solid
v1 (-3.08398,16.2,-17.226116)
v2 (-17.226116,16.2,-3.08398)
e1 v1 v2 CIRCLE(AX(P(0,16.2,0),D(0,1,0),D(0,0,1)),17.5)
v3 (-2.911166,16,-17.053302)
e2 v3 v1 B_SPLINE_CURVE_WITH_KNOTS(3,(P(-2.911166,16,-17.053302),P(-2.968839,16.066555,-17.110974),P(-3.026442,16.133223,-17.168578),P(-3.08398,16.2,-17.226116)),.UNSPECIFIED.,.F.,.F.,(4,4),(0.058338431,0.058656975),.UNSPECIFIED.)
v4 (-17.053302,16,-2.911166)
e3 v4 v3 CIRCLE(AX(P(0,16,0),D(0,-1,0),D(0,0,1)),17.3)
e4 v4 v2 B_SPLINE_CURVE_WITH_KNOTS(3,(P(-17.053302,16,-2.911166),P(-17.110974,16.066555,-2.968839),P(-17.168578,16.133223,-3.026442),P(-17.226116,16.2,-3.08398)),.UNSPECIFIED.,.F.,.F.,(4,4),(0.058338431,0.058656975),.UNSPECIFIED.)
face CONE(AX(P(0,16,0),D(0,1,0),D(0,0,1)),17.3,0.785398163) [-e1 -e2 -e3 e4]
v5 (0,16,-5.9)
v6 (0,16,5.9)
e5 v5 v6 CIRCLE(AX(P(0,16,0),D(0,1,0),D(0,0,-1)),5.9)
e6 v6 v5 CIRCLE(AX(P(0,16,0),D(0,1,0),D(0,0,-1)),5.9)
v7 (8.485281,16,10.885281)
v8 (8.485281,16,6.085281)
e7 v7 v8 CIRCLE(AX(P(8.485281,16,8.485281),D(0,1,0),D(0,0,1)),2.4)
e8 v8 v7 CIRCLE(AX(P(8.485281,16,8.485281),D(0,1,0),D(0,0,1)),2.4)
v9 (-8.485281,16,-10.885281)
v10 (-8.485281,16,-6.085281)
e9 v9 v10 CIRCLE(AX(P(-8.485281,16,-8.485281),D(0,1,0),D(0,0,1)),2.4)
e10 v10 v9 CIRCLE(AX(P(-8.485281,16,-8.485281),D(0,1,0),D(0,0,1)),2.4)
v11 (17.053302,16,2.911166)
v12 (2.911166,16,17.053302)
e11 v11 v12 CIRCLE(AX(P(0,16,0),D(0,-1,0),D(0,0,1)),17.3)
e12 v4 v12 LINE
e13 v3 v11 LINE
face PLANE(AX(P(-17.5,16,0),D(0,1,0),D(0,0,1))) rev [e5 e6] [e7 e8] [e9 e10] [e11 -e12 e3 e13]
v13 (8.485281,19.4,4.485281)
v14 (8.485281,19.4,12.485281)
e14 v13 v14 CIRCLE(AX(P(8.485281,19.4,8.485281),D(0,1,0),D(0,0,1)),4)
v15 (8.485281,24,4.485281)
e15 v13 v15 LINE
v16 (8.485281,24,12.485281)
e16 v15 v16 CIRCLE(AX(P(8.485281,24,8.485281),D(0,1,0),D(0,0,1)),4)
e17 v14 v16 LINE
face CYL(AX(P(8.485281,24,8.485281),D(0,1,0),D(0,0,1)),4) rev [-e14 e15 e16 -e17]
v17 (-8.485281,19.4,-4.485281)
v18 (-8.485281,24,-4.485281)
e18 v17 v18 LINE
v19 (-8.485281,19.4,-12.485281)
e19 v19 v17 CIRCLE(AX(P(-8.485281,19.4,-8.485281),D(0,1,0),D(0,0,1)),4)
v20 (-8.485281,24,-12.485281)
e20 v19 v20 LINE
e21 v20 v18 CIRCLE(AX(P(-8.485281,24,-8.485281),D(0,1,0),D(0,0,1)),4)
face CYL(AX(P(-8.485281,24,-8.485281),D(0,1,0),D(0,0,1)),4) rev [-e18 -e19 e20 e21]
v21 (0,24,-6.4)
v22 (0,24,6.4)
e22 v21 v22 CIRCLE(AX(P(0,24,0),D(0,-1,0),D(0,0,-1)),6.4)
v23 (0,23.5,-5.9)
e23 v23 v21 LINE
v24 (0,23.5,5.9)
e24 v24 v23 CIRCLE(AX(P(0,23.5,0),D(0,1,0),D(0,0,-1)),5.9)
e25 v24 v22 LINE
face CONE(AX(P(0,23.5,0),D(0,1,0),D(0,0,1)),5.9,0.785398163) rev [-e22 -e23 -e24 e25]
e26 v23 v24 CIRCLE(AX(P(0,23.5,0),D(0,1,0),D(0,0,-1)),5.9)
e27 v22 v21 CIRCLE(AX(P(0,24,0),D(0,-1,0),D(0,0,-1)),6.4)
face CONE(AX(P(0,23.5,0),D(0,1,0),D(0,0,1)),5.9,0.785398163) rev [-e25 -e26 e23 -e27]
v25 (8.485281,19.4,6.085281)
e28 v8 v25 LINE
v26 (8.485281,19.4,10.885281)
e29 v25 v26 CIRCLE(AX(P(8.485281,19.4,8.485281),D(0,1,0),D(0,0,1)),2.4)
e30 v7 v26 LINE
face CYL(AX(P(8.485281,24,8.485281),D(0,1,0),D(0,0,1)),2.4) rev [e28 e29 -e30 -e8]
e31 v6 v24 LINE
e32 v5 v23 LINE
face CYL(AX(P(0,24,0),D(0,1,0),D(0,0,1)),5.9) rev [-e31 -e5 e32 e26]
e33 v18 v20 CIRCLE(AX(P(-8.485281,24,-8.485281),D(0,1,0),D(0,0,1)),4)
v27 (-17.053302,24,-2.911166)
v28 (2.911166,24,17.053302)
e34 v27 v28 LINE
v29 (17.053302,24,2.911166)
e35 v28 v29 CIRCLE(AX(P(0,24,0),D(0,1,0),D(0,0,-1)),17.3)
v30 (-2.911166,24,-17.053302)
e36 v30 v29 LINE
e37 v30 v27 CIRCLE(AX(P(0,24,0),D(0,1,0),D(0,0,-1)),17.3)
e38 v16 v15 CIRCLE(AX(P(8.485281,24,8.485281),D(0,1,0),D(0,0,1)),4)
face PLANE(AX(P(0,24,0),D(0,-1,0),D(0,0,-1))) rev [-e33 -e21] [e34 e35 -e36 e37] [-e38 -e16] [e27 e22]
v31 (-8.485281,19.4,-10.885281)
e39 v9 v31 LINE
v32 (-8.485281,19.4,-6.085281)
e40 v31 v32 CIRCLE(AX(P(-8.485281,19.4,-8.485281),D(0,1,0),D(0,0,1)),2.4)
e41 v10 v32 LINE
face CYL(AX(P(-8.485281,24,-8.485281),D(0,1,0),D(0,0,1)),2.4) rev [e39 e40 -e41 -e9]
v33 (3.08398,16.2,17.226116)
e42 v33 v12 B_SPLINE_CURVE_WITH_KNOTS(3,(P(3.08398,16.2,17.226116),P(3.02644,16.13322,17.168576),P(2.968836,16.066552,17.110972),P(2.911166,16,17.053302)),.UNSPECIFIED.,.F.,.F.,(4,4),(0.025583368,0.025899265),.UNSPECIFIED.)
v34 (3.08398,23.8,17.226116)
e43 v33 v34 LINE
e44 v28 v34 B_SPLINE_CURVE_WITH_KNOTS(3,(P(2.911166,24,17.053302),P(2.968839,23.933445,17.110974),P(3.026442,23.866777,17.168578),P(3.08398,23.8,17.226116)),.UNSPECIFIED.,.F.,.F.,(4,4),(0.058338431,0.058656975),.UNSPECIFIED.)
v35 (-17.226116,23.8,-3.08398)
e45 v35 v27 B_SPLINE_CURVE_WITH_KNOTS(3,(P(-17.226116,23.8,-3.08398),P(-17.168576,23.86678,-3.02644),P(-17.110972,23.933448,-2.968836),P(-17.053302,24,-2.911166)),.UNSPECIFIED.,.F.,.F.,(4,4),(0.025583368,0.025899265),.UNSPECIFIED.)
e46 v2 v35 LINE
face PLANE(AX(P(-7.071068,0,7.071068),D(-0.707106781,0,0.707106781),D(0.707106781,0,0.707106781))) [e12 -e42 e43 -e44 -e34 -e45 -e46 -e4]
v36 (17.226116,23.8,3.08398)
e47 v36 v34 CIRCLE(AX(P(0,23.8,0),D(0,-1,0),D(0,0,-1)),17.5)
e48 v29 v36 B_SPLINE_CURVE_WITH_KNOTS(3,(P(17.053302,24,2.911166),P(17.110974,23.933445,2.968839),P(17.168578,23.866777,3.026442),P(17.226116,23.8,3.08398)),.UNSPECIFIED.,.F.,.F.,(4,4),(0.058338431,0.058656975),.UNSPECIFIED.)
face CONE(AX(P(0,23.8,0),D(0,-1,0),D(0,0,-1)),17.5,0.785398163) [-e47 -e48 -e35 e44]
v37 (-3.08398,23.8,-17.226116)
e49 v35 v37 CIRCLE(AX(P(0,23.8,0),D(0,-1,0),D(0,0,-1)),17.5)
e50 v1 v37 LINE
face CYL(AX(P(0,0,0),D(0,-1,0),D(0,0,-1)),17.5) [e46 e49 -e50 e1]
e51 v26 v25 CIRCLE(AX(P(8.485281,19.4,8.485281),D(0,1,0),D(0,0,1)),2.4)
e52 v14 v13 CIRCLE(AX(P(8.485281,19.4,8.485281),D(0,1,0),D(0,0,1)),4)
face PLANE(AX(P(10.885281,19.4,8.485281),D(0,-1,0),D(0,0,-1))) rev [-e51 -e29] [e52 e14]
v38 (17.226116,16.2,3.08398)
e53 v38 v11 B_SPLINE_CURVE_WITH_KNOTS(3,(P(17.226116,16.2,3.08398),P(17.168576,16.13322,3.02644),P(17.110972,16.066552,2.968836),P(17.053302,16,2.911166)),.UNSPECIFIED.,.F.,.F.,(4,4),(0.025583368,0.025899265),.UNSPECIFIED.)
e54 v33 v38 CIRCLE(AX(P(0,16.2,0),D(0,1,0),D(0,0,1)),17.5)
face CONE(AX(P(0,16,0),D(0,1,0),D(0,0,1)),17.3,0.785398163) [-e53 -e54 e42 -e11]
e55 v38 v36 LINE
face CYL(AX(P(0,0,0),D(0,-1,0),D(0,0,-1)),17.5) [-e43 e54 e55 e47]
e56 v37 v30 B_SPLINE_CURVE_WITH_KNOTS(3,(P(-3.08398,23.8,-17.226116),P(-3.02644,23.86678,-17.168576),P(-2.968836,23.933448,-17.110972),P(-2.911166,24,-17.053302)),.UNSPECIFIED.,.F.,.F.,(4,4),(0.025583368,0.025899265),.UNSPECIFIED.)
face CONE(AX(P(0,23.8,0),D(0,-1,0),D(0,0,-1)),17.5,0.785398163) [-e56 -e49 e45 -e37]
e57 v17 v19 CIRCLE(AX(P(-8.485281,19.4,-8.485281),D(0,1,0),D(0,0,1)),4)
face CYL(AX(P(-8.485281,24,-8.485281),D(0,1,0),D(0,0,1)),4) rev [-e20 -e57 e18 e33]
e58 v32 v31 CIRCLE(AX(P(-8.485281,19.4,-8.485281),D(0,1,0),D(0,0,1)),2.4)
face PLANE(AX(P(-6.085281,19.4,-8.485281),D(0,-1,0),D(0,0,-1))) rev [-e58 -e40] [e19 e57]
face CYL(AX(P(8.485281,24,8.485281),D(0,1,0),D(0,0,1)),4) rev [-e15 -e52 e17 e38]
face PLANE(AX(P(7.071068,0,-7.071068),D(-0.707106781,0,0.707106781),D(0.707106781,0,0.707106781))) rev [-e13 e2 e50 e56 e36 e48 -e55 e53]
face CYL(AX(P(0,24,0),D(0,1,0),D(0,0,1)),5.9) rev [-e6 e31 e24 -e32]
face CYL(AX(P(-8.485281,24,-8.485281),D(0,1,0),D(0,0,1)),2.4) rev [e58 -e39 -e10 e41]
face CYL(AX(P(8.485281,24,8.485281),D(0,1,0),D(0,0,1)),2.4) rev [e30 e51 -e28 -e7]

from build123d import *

# Parameters (mm, degrees)
G1_4_TAPPED_HOLE1_D                               = 11.8
HOLE_SIZE_BASED_ON_SOCKET_HEAD_CAP_SC_D           = 4.8
HOLE_SIZE_BASED_ON_SOCKET_HEAD_CAP_SC_CBORE_D     = 8
HOLE_SIZE_BASED_ON_SOCKET_HEAD_CAP_SC_CBORE_DEPTH = 4.6
FILLET1_R                                         = 0.2
CHAMFER1_SIZE                                     = 0.2
CHAMFER2_SIZE                                     = 0.5
CUT_EXTRUDE1_DEPTH                                = 35.474628352
SKETCH8_R                                         = 15
CUT_EXTRUDE2_DEPTH                                = 30.145808143


with BuildPart() as part:
    # Sketch2 → Revolve1 (revolve)
    with BuildSketch(Plane.XY, mode=Mode.PRIVATE) as revolve1_sk:
        Polygon((0, 24), (-17.5, 24), (-17.5, 16), (-6.75, 16), (-6.75, 0), (0, 0), align=None)
    revolve(revolve1_sk.sketch.rotate(Axis((0, 0, 0), (0, 1, 0)), 270), axis=Axis((0, 0, 0), (0, 1, 0)))

    # G1/4 Tapped Hole1 (through all)
    with Locations(Plane.ZX.offset(24)):
        with Locations((0, 0)):
            Hole(G1_4_TAPPED_HOLE1_D / 2)

    # Hole Size (% based on) Socket Head Cap Screw Type 1 (through all)
    with Locations(Plane(origin=(-8.485281374, 24, -8.485281374), x_dir=(0, 0, 1), z_dir=(0, 1, 0))):
        with Locations((0, 0), (16.970562748, 16.970562748)):
            CounterBoreHole(HOLE_SIZE_BASED_ON_SOCKET_HEAD_CAP_SC_D / 2, HOLE_SIZE_BASED_ON_SOCKET_HEAD_CAP_SC_CBORE_D / 2, HOLE_SIZE_BASED_ON_SOCKET_HEAD_CAP_SC_CBORE_DEPTH)

    # Fillet1
    fillet1_edges = [part.edges().sort_by_distance(p)[0] for p in [
        (0, 16, 6.75),
    ]]
    fillet(fillet1_edges, radius=FILLET1_R)

    # Chamfer1
    chamfer1_edges = [part.edges().sort_by_distance(p)[0] for p in [
        (0, 0, 6.75),
        (0, 16, 17.5),
        (0, 24, 17.5),
    ]]
    chamfer(chamfer1_edges, length=CHAMFER1_SIZE)

    # Chamfer2
    chamfer2_edges = [part.edges().sort_by_distance(p)[0] for p in [
        (0, 24, 5.9),
        (0, 0, 5.9),
    ]]
    chamfer(chamfer2_edges, length=CHAMFER2_SIZE)

    # Sketch7 → Cut-Extrude1 (cut, through all)
    with BuildSketch(Plane(origin=(0, 24, 0), x_dir=(1, 0, 0), z_dir=(0, 1, 0))):
        with BuildLine():
            Line((2.911166407, -17.053302031), (-17.053302031, 2.911166407))
            ThreePointArc((-17.053302031, 2.911166407), (-12.232947315, -12.232947315), (2.911166407, -17.053302031))
        make_face()
        with BuildLine():
            ThreePointArc((17.3, 0), (11.156317071, 13.222200627), (-2.911166407, 17.053302031))
            Line((-2.911166407, 17.053302031), (17.053302031, -2.911166407))
            ThreePointArc((17.053302031, -2.911166407), (17.238215179, -1.460800272), (17.3, 0))
        make_face()
        with BuildLine():
            Line((-17.053302031, 2.911166407), (-17.226115818, 3.083980194))
            ThreePointArc((-17.226115818, 3.083980194), (-12.374368671, -12.374368671), (3.083980194, -17.226115818))
            Line((3.083980194, -17.226115818), (2.911166407, -17.053302031))
            ThreePointArc((2.911166407, -17.053302031), (-12.232947315, -12.232947315), (-17.053302031, 2.911166407))
        make_face()
        with BuildLine():
            ThreePointArc((17.5, 0), (11.23121424, 13.42050024), (-3.083980194, 17.226115818))
            Line((-3.083980194, 17.226115818), (-2.911166407, 17.053302031))
            ThreePointArc((-2.911166407, 17.053302031), (11.156317071, 13.222200627), (17.3, 0))
            ThreePointArc((17.3, 0), (17.238215179, -1.460800272), (17.053302031, -2.911166407))
            Line((17.053302031, -2.911166407), (17.226115818, -3.083980194))
            ThreePointArc((17.226115818, -3.083980194), (17.431394477, -1.548058977), (17.5, 0))
        make_face()
    extrude(amount=-CUT_EXTRUDE1_DEPTH, mode=Mode.SUBTRACT)

    # Sketch8 → Cut-Extrude2 (cut, through all)
    with BuildSketch(Plane.XZ.offset(-16)):
        Circle(SKETCH8_R)
    extrude(amount=CUT_EXTRUDE2_DEPTH, mode=Mode.SUBTRACT)


solid = part.part
